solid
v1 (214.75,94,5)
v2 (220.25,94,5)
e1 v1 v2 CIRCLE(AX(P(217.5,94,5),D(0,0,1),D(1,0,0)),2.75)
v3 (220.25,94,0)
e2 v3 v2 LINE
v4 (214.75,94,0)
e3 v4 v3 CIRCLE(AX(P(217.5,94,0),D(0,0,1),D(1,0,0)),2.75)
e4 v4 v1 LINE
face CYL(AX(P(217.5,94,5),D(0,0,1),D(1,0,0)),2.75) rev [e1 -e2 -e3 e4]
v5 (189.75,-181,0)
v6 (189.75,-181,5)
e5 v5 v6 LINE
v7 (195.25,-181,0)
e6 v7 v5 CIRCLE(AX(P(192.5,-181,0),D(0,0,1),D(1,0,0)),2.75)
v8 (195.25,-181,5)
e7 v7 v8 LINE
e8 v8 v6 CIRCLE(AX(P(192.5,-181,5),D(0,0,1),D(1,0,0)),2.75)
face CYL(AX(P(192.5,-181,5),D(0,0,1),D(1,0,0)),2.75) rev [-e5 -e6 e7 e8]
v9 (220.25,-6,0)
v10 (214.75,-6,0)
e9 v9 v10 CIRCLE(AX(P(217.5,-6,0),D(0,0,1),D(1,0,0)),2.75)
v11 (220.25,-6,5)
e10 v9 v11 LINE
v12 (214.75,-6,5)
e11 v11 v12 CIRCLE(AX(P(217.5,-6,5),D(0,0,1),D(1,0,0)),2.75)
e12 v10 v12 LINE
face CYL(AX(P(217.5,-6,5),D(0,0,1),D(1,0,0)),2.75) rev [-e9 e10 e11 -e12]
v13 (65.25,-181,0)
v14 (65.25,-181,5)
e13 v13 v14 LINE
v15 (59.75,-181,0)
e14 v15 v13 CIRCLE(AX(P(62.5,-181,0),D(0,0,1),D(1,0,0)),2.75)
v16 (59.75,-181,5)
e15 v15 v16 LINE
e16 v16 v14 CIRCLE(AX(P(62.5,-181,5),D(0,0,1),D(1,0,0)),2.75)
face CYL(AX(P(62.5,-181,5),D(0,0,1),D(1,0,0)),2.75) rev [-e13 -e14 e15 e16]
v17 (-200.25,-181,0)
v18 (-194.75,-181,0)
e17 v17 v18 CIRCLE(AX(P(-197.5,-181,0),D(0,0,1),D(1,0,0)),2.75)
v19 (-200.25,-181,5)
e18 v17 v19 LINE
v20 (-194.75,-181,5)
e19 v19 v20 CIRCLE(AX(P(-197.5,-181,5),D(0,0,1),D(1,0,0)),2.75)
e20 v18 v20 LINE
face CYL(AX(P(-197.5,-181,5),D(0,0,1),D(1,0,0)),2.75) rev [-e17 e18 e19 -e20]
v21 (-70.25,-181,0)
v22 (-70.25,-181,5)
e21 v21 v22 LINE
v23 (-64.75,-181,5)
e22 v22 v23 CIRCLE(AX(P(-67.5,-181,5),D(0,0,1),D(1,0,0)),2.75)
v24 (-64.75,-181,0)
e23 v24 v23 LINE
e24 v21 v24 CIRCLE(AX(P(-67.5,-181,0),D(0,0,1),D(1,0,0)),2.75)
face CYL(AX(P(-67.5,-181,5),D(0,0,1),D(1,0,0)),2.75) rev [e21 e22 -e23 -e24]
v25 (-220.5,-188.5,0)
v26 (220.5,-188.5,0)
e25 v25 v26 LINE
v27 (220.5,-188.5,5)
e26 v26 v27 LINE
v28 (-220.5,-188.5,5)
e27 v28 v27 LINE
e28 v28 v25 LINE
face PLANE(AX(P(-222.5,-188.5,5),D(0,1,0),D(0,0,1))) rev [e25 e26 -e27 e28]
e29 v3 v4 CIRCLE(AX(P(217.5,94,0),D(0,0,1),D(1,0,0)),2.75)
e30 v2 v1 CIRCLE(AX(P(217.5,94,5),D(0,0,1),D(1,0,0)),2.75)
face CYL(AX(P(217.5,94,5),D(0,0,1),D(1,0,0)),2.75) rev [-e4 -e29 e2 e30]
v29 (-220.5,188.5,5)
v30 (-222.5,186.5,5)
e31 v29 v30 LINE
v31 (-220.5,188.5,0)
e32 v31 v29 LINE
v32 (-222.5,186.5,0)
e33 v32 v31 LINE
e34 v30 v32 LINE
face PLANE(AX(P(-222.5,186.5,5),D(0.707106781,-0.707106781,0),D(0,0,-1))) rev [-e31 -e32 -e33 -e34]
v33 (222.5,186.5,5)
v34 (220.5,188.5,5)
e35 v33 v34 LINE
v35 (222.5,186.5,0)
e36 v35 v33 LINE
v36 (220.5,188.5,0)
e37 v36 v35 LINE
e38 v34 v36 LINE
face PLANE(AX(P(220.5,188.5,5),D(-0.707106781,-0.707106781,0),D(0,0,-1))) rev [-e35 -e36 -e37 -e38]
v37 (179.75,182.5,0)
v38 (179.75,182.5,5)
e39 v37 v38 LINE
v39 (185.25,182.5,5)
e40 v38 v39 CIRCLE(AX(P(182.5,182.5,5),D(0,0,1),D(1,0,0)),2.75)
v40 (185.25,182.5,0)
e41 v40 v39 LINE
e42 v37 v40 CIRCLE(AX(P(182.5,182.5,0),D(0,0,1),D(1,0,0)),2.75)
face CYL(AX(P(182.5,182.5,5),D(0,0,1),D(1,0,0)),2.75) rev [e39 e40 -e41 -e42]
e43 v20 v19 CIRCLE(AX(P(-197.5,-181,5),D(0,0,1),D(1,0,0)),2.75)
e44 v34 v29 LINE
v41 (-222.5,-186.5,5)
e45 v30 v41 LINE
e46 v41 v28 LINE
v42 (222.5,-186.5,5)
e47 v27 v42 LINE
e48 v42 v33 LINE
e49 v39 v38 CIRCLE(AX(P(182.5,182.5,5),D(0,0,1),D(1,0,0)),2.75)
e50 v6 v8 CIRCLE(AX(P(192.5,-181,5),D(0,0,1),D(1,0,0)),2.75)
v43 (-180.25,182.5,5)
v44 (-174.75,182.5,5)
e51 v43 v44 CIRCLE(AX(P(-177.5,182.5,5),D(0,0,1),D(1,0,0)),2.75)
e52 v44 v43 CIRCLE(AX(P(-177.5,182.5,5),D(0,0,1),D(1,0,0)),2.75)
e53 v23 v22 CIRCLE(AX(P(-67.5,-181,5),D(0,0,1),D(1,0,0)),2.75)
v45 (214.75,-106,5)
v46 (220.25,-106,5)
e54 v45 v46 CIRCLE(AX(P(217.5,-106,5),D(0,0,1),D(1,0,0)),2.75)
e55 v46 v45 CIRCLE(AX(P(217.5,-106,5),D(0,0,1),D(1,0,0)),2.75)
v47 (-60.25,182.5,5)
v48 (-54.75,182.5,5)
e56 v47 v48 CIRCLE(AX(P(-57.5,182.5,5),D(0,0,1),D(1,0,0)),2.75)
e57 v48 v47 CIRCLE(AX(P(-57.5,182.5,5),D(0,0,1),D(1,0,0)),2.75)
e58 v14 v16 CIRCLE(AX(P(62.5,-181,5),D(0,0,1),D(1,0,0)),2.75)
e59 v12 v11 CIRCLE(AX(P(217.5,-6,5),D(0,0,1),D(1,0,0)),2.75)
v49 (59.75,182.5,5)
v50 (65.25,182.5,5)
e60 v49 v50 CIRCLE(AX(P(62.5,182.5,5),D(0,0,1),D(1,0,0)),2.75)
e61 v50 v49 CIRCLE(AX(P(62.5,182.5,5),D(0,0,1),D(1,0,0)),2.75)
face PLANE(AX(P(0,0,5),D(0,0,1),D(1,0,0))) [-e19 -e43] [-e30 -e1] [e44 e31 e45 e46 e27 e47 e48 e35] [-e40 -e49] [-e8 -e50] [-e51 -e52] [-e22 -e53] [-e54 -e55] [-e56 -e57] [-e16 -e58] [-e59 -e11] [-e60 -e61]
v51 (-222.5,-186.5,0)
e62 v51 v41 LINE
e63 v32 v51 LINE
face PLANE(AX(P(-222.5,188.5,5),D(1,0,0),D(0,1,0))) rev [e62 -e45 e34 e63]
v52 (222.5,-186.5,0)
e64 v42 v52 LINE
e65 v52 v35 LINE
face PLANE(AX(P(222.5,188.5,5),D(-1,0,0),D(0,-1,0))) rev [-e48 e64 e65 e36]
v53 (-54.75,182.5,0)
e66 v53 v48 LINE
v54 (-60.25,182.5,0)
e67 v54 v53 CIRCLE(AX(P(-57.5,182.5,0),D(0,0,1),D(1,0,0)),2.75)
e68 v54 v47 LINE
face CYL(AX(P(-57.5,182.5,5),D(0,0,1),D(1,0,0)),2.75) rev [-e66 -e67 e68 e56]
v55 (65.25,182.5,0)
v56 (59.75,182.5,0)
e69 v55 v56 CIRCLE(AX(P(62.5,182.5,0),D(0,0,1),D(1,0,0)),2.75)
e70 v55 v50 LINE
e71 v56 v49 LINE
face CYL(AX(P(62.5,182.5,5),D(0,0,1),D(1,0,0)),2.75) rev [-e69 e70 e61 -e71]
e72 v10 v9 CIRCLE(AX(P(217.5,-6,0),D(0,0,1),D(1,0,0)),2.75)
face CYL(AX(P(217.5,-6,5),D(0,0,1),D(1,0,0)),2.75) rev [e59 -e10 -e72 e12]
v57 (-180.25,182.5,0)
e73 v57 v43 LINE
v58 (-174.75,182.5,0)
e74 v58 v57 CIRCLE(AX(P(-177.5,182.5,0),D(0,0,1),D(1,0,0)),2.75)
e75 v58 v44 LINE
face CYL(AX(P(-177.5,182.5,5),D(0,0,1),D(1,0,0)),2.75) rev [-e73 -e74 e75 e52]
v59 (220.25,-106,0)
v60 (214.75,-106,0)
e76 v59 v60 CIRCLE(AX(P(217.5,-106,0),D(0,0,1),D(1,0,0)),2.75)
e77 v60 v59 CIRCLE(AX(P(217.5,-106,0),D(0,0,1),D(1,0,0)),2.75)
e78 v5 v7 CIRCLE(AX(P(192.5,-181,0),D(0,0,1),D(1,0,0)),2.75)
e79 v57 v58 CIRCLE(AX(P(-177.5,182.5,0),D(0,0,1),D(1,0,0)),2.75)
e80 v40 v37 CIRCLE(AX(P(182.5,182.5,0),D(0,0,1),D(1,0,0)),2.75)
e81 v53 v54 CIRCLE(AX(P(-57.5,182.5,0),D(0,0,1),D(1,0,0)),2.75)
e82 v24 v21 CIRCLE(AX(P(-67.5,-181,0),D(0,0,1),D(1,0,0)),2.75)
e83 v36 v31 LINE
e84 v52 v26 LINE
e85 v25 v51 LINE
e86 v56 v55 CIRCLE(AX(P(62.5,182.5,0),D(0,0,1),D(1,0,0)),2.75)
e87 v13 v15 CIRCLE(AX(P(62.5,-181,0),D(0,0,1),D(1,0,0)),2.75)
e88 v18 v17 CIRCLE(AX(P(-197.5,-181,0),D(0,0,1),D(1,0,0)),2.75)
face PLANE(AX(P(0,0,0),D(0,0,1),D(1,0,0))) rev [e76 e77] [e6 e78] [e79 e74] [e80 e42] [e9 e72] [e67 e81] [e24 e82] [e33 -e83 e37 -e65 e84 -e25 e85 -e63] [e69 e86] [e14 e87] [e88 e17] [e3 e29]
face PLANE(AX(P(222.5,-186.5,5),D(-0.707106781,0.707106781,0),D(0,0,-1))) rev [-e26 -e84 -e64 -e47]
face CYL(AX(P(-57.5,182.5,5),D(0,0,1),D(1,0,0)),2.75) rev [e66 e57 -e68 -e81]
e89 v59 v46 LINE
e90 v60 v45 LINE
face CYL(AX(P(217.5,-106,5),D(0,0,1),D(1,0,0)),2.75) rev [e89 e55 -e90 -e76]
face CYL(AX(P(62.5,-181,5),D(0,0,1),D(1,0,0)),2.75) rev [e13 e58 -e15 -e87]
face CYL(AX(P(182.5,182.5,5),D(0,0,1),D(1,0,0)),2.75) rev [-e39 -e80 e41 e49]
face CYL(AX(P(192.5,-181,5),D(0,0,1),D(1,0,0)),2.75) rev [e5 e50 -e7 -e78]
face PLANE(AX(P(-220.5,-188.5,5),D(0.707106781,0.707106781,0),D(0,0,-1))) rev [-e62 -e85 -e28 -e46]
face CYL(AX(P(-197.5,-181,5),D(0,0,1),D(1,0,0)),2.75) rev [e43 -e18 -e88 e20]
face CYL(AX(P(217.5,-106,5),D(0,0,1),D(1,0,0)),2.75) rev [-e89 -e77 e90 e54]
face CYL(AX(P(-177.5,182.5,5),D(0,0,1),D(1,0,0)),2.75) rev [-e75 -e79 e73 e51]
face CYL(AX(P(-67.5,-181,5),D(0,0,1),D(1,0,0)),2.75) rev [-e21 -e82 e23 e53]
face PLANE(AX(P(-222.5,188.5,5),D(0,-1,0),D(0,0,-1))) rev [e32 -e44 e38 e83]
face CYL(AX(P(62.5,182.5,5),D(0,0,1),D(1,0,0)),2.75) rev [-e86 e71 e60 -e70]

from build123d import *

# Parameters (mm, degrees)
SKETCH1_W            = 445
SKETCH1_H            = 377
BOSS_EXTRUDE1_DEPTH  = 5
M5_CLEARANCE_HOLE1_D = 5.5
FILLET1_SIZE         = 2


with BuildPart() as part:
    # Sketch1 → Boss-Extrude1 (new body)
    with BuildSketch(Plane.XY):
        Rectangle(SKETCH1_W, SKETCH1_H)
    extrude(amount=BOSS_EXTRUDE1_DEPTH)

    # M5 Clearance Hole1 (through all)
    with Locations(Plane.XY.offset(5)):
        with Locations((-177.5, 182.5), (-57.5, 182.5), (62.5, 182.5), (182.5, 182.5), (-197.5, -181), (-67.5, -181), (62.5, -181), (192.5, -181), (217.5, -106), (217.5, -6), (217.5, 94)):
            Hole(M5_CLEARANCE_HOLE1_D / 2)

    # Fillet1
    fillet1_edges = [part.edges().sort_by_distance(p)[0] for p in [
        (222.5, -188.5, 2.5),
        (-222.5, -188.5, 2.5),
        (-222.5, 188.5, 2.5),
        (222.5, 188.5, 2.5),
    ]]
    chamfer(fillet1_edges, length=FILLET1_SIZE)


solid = part.part
